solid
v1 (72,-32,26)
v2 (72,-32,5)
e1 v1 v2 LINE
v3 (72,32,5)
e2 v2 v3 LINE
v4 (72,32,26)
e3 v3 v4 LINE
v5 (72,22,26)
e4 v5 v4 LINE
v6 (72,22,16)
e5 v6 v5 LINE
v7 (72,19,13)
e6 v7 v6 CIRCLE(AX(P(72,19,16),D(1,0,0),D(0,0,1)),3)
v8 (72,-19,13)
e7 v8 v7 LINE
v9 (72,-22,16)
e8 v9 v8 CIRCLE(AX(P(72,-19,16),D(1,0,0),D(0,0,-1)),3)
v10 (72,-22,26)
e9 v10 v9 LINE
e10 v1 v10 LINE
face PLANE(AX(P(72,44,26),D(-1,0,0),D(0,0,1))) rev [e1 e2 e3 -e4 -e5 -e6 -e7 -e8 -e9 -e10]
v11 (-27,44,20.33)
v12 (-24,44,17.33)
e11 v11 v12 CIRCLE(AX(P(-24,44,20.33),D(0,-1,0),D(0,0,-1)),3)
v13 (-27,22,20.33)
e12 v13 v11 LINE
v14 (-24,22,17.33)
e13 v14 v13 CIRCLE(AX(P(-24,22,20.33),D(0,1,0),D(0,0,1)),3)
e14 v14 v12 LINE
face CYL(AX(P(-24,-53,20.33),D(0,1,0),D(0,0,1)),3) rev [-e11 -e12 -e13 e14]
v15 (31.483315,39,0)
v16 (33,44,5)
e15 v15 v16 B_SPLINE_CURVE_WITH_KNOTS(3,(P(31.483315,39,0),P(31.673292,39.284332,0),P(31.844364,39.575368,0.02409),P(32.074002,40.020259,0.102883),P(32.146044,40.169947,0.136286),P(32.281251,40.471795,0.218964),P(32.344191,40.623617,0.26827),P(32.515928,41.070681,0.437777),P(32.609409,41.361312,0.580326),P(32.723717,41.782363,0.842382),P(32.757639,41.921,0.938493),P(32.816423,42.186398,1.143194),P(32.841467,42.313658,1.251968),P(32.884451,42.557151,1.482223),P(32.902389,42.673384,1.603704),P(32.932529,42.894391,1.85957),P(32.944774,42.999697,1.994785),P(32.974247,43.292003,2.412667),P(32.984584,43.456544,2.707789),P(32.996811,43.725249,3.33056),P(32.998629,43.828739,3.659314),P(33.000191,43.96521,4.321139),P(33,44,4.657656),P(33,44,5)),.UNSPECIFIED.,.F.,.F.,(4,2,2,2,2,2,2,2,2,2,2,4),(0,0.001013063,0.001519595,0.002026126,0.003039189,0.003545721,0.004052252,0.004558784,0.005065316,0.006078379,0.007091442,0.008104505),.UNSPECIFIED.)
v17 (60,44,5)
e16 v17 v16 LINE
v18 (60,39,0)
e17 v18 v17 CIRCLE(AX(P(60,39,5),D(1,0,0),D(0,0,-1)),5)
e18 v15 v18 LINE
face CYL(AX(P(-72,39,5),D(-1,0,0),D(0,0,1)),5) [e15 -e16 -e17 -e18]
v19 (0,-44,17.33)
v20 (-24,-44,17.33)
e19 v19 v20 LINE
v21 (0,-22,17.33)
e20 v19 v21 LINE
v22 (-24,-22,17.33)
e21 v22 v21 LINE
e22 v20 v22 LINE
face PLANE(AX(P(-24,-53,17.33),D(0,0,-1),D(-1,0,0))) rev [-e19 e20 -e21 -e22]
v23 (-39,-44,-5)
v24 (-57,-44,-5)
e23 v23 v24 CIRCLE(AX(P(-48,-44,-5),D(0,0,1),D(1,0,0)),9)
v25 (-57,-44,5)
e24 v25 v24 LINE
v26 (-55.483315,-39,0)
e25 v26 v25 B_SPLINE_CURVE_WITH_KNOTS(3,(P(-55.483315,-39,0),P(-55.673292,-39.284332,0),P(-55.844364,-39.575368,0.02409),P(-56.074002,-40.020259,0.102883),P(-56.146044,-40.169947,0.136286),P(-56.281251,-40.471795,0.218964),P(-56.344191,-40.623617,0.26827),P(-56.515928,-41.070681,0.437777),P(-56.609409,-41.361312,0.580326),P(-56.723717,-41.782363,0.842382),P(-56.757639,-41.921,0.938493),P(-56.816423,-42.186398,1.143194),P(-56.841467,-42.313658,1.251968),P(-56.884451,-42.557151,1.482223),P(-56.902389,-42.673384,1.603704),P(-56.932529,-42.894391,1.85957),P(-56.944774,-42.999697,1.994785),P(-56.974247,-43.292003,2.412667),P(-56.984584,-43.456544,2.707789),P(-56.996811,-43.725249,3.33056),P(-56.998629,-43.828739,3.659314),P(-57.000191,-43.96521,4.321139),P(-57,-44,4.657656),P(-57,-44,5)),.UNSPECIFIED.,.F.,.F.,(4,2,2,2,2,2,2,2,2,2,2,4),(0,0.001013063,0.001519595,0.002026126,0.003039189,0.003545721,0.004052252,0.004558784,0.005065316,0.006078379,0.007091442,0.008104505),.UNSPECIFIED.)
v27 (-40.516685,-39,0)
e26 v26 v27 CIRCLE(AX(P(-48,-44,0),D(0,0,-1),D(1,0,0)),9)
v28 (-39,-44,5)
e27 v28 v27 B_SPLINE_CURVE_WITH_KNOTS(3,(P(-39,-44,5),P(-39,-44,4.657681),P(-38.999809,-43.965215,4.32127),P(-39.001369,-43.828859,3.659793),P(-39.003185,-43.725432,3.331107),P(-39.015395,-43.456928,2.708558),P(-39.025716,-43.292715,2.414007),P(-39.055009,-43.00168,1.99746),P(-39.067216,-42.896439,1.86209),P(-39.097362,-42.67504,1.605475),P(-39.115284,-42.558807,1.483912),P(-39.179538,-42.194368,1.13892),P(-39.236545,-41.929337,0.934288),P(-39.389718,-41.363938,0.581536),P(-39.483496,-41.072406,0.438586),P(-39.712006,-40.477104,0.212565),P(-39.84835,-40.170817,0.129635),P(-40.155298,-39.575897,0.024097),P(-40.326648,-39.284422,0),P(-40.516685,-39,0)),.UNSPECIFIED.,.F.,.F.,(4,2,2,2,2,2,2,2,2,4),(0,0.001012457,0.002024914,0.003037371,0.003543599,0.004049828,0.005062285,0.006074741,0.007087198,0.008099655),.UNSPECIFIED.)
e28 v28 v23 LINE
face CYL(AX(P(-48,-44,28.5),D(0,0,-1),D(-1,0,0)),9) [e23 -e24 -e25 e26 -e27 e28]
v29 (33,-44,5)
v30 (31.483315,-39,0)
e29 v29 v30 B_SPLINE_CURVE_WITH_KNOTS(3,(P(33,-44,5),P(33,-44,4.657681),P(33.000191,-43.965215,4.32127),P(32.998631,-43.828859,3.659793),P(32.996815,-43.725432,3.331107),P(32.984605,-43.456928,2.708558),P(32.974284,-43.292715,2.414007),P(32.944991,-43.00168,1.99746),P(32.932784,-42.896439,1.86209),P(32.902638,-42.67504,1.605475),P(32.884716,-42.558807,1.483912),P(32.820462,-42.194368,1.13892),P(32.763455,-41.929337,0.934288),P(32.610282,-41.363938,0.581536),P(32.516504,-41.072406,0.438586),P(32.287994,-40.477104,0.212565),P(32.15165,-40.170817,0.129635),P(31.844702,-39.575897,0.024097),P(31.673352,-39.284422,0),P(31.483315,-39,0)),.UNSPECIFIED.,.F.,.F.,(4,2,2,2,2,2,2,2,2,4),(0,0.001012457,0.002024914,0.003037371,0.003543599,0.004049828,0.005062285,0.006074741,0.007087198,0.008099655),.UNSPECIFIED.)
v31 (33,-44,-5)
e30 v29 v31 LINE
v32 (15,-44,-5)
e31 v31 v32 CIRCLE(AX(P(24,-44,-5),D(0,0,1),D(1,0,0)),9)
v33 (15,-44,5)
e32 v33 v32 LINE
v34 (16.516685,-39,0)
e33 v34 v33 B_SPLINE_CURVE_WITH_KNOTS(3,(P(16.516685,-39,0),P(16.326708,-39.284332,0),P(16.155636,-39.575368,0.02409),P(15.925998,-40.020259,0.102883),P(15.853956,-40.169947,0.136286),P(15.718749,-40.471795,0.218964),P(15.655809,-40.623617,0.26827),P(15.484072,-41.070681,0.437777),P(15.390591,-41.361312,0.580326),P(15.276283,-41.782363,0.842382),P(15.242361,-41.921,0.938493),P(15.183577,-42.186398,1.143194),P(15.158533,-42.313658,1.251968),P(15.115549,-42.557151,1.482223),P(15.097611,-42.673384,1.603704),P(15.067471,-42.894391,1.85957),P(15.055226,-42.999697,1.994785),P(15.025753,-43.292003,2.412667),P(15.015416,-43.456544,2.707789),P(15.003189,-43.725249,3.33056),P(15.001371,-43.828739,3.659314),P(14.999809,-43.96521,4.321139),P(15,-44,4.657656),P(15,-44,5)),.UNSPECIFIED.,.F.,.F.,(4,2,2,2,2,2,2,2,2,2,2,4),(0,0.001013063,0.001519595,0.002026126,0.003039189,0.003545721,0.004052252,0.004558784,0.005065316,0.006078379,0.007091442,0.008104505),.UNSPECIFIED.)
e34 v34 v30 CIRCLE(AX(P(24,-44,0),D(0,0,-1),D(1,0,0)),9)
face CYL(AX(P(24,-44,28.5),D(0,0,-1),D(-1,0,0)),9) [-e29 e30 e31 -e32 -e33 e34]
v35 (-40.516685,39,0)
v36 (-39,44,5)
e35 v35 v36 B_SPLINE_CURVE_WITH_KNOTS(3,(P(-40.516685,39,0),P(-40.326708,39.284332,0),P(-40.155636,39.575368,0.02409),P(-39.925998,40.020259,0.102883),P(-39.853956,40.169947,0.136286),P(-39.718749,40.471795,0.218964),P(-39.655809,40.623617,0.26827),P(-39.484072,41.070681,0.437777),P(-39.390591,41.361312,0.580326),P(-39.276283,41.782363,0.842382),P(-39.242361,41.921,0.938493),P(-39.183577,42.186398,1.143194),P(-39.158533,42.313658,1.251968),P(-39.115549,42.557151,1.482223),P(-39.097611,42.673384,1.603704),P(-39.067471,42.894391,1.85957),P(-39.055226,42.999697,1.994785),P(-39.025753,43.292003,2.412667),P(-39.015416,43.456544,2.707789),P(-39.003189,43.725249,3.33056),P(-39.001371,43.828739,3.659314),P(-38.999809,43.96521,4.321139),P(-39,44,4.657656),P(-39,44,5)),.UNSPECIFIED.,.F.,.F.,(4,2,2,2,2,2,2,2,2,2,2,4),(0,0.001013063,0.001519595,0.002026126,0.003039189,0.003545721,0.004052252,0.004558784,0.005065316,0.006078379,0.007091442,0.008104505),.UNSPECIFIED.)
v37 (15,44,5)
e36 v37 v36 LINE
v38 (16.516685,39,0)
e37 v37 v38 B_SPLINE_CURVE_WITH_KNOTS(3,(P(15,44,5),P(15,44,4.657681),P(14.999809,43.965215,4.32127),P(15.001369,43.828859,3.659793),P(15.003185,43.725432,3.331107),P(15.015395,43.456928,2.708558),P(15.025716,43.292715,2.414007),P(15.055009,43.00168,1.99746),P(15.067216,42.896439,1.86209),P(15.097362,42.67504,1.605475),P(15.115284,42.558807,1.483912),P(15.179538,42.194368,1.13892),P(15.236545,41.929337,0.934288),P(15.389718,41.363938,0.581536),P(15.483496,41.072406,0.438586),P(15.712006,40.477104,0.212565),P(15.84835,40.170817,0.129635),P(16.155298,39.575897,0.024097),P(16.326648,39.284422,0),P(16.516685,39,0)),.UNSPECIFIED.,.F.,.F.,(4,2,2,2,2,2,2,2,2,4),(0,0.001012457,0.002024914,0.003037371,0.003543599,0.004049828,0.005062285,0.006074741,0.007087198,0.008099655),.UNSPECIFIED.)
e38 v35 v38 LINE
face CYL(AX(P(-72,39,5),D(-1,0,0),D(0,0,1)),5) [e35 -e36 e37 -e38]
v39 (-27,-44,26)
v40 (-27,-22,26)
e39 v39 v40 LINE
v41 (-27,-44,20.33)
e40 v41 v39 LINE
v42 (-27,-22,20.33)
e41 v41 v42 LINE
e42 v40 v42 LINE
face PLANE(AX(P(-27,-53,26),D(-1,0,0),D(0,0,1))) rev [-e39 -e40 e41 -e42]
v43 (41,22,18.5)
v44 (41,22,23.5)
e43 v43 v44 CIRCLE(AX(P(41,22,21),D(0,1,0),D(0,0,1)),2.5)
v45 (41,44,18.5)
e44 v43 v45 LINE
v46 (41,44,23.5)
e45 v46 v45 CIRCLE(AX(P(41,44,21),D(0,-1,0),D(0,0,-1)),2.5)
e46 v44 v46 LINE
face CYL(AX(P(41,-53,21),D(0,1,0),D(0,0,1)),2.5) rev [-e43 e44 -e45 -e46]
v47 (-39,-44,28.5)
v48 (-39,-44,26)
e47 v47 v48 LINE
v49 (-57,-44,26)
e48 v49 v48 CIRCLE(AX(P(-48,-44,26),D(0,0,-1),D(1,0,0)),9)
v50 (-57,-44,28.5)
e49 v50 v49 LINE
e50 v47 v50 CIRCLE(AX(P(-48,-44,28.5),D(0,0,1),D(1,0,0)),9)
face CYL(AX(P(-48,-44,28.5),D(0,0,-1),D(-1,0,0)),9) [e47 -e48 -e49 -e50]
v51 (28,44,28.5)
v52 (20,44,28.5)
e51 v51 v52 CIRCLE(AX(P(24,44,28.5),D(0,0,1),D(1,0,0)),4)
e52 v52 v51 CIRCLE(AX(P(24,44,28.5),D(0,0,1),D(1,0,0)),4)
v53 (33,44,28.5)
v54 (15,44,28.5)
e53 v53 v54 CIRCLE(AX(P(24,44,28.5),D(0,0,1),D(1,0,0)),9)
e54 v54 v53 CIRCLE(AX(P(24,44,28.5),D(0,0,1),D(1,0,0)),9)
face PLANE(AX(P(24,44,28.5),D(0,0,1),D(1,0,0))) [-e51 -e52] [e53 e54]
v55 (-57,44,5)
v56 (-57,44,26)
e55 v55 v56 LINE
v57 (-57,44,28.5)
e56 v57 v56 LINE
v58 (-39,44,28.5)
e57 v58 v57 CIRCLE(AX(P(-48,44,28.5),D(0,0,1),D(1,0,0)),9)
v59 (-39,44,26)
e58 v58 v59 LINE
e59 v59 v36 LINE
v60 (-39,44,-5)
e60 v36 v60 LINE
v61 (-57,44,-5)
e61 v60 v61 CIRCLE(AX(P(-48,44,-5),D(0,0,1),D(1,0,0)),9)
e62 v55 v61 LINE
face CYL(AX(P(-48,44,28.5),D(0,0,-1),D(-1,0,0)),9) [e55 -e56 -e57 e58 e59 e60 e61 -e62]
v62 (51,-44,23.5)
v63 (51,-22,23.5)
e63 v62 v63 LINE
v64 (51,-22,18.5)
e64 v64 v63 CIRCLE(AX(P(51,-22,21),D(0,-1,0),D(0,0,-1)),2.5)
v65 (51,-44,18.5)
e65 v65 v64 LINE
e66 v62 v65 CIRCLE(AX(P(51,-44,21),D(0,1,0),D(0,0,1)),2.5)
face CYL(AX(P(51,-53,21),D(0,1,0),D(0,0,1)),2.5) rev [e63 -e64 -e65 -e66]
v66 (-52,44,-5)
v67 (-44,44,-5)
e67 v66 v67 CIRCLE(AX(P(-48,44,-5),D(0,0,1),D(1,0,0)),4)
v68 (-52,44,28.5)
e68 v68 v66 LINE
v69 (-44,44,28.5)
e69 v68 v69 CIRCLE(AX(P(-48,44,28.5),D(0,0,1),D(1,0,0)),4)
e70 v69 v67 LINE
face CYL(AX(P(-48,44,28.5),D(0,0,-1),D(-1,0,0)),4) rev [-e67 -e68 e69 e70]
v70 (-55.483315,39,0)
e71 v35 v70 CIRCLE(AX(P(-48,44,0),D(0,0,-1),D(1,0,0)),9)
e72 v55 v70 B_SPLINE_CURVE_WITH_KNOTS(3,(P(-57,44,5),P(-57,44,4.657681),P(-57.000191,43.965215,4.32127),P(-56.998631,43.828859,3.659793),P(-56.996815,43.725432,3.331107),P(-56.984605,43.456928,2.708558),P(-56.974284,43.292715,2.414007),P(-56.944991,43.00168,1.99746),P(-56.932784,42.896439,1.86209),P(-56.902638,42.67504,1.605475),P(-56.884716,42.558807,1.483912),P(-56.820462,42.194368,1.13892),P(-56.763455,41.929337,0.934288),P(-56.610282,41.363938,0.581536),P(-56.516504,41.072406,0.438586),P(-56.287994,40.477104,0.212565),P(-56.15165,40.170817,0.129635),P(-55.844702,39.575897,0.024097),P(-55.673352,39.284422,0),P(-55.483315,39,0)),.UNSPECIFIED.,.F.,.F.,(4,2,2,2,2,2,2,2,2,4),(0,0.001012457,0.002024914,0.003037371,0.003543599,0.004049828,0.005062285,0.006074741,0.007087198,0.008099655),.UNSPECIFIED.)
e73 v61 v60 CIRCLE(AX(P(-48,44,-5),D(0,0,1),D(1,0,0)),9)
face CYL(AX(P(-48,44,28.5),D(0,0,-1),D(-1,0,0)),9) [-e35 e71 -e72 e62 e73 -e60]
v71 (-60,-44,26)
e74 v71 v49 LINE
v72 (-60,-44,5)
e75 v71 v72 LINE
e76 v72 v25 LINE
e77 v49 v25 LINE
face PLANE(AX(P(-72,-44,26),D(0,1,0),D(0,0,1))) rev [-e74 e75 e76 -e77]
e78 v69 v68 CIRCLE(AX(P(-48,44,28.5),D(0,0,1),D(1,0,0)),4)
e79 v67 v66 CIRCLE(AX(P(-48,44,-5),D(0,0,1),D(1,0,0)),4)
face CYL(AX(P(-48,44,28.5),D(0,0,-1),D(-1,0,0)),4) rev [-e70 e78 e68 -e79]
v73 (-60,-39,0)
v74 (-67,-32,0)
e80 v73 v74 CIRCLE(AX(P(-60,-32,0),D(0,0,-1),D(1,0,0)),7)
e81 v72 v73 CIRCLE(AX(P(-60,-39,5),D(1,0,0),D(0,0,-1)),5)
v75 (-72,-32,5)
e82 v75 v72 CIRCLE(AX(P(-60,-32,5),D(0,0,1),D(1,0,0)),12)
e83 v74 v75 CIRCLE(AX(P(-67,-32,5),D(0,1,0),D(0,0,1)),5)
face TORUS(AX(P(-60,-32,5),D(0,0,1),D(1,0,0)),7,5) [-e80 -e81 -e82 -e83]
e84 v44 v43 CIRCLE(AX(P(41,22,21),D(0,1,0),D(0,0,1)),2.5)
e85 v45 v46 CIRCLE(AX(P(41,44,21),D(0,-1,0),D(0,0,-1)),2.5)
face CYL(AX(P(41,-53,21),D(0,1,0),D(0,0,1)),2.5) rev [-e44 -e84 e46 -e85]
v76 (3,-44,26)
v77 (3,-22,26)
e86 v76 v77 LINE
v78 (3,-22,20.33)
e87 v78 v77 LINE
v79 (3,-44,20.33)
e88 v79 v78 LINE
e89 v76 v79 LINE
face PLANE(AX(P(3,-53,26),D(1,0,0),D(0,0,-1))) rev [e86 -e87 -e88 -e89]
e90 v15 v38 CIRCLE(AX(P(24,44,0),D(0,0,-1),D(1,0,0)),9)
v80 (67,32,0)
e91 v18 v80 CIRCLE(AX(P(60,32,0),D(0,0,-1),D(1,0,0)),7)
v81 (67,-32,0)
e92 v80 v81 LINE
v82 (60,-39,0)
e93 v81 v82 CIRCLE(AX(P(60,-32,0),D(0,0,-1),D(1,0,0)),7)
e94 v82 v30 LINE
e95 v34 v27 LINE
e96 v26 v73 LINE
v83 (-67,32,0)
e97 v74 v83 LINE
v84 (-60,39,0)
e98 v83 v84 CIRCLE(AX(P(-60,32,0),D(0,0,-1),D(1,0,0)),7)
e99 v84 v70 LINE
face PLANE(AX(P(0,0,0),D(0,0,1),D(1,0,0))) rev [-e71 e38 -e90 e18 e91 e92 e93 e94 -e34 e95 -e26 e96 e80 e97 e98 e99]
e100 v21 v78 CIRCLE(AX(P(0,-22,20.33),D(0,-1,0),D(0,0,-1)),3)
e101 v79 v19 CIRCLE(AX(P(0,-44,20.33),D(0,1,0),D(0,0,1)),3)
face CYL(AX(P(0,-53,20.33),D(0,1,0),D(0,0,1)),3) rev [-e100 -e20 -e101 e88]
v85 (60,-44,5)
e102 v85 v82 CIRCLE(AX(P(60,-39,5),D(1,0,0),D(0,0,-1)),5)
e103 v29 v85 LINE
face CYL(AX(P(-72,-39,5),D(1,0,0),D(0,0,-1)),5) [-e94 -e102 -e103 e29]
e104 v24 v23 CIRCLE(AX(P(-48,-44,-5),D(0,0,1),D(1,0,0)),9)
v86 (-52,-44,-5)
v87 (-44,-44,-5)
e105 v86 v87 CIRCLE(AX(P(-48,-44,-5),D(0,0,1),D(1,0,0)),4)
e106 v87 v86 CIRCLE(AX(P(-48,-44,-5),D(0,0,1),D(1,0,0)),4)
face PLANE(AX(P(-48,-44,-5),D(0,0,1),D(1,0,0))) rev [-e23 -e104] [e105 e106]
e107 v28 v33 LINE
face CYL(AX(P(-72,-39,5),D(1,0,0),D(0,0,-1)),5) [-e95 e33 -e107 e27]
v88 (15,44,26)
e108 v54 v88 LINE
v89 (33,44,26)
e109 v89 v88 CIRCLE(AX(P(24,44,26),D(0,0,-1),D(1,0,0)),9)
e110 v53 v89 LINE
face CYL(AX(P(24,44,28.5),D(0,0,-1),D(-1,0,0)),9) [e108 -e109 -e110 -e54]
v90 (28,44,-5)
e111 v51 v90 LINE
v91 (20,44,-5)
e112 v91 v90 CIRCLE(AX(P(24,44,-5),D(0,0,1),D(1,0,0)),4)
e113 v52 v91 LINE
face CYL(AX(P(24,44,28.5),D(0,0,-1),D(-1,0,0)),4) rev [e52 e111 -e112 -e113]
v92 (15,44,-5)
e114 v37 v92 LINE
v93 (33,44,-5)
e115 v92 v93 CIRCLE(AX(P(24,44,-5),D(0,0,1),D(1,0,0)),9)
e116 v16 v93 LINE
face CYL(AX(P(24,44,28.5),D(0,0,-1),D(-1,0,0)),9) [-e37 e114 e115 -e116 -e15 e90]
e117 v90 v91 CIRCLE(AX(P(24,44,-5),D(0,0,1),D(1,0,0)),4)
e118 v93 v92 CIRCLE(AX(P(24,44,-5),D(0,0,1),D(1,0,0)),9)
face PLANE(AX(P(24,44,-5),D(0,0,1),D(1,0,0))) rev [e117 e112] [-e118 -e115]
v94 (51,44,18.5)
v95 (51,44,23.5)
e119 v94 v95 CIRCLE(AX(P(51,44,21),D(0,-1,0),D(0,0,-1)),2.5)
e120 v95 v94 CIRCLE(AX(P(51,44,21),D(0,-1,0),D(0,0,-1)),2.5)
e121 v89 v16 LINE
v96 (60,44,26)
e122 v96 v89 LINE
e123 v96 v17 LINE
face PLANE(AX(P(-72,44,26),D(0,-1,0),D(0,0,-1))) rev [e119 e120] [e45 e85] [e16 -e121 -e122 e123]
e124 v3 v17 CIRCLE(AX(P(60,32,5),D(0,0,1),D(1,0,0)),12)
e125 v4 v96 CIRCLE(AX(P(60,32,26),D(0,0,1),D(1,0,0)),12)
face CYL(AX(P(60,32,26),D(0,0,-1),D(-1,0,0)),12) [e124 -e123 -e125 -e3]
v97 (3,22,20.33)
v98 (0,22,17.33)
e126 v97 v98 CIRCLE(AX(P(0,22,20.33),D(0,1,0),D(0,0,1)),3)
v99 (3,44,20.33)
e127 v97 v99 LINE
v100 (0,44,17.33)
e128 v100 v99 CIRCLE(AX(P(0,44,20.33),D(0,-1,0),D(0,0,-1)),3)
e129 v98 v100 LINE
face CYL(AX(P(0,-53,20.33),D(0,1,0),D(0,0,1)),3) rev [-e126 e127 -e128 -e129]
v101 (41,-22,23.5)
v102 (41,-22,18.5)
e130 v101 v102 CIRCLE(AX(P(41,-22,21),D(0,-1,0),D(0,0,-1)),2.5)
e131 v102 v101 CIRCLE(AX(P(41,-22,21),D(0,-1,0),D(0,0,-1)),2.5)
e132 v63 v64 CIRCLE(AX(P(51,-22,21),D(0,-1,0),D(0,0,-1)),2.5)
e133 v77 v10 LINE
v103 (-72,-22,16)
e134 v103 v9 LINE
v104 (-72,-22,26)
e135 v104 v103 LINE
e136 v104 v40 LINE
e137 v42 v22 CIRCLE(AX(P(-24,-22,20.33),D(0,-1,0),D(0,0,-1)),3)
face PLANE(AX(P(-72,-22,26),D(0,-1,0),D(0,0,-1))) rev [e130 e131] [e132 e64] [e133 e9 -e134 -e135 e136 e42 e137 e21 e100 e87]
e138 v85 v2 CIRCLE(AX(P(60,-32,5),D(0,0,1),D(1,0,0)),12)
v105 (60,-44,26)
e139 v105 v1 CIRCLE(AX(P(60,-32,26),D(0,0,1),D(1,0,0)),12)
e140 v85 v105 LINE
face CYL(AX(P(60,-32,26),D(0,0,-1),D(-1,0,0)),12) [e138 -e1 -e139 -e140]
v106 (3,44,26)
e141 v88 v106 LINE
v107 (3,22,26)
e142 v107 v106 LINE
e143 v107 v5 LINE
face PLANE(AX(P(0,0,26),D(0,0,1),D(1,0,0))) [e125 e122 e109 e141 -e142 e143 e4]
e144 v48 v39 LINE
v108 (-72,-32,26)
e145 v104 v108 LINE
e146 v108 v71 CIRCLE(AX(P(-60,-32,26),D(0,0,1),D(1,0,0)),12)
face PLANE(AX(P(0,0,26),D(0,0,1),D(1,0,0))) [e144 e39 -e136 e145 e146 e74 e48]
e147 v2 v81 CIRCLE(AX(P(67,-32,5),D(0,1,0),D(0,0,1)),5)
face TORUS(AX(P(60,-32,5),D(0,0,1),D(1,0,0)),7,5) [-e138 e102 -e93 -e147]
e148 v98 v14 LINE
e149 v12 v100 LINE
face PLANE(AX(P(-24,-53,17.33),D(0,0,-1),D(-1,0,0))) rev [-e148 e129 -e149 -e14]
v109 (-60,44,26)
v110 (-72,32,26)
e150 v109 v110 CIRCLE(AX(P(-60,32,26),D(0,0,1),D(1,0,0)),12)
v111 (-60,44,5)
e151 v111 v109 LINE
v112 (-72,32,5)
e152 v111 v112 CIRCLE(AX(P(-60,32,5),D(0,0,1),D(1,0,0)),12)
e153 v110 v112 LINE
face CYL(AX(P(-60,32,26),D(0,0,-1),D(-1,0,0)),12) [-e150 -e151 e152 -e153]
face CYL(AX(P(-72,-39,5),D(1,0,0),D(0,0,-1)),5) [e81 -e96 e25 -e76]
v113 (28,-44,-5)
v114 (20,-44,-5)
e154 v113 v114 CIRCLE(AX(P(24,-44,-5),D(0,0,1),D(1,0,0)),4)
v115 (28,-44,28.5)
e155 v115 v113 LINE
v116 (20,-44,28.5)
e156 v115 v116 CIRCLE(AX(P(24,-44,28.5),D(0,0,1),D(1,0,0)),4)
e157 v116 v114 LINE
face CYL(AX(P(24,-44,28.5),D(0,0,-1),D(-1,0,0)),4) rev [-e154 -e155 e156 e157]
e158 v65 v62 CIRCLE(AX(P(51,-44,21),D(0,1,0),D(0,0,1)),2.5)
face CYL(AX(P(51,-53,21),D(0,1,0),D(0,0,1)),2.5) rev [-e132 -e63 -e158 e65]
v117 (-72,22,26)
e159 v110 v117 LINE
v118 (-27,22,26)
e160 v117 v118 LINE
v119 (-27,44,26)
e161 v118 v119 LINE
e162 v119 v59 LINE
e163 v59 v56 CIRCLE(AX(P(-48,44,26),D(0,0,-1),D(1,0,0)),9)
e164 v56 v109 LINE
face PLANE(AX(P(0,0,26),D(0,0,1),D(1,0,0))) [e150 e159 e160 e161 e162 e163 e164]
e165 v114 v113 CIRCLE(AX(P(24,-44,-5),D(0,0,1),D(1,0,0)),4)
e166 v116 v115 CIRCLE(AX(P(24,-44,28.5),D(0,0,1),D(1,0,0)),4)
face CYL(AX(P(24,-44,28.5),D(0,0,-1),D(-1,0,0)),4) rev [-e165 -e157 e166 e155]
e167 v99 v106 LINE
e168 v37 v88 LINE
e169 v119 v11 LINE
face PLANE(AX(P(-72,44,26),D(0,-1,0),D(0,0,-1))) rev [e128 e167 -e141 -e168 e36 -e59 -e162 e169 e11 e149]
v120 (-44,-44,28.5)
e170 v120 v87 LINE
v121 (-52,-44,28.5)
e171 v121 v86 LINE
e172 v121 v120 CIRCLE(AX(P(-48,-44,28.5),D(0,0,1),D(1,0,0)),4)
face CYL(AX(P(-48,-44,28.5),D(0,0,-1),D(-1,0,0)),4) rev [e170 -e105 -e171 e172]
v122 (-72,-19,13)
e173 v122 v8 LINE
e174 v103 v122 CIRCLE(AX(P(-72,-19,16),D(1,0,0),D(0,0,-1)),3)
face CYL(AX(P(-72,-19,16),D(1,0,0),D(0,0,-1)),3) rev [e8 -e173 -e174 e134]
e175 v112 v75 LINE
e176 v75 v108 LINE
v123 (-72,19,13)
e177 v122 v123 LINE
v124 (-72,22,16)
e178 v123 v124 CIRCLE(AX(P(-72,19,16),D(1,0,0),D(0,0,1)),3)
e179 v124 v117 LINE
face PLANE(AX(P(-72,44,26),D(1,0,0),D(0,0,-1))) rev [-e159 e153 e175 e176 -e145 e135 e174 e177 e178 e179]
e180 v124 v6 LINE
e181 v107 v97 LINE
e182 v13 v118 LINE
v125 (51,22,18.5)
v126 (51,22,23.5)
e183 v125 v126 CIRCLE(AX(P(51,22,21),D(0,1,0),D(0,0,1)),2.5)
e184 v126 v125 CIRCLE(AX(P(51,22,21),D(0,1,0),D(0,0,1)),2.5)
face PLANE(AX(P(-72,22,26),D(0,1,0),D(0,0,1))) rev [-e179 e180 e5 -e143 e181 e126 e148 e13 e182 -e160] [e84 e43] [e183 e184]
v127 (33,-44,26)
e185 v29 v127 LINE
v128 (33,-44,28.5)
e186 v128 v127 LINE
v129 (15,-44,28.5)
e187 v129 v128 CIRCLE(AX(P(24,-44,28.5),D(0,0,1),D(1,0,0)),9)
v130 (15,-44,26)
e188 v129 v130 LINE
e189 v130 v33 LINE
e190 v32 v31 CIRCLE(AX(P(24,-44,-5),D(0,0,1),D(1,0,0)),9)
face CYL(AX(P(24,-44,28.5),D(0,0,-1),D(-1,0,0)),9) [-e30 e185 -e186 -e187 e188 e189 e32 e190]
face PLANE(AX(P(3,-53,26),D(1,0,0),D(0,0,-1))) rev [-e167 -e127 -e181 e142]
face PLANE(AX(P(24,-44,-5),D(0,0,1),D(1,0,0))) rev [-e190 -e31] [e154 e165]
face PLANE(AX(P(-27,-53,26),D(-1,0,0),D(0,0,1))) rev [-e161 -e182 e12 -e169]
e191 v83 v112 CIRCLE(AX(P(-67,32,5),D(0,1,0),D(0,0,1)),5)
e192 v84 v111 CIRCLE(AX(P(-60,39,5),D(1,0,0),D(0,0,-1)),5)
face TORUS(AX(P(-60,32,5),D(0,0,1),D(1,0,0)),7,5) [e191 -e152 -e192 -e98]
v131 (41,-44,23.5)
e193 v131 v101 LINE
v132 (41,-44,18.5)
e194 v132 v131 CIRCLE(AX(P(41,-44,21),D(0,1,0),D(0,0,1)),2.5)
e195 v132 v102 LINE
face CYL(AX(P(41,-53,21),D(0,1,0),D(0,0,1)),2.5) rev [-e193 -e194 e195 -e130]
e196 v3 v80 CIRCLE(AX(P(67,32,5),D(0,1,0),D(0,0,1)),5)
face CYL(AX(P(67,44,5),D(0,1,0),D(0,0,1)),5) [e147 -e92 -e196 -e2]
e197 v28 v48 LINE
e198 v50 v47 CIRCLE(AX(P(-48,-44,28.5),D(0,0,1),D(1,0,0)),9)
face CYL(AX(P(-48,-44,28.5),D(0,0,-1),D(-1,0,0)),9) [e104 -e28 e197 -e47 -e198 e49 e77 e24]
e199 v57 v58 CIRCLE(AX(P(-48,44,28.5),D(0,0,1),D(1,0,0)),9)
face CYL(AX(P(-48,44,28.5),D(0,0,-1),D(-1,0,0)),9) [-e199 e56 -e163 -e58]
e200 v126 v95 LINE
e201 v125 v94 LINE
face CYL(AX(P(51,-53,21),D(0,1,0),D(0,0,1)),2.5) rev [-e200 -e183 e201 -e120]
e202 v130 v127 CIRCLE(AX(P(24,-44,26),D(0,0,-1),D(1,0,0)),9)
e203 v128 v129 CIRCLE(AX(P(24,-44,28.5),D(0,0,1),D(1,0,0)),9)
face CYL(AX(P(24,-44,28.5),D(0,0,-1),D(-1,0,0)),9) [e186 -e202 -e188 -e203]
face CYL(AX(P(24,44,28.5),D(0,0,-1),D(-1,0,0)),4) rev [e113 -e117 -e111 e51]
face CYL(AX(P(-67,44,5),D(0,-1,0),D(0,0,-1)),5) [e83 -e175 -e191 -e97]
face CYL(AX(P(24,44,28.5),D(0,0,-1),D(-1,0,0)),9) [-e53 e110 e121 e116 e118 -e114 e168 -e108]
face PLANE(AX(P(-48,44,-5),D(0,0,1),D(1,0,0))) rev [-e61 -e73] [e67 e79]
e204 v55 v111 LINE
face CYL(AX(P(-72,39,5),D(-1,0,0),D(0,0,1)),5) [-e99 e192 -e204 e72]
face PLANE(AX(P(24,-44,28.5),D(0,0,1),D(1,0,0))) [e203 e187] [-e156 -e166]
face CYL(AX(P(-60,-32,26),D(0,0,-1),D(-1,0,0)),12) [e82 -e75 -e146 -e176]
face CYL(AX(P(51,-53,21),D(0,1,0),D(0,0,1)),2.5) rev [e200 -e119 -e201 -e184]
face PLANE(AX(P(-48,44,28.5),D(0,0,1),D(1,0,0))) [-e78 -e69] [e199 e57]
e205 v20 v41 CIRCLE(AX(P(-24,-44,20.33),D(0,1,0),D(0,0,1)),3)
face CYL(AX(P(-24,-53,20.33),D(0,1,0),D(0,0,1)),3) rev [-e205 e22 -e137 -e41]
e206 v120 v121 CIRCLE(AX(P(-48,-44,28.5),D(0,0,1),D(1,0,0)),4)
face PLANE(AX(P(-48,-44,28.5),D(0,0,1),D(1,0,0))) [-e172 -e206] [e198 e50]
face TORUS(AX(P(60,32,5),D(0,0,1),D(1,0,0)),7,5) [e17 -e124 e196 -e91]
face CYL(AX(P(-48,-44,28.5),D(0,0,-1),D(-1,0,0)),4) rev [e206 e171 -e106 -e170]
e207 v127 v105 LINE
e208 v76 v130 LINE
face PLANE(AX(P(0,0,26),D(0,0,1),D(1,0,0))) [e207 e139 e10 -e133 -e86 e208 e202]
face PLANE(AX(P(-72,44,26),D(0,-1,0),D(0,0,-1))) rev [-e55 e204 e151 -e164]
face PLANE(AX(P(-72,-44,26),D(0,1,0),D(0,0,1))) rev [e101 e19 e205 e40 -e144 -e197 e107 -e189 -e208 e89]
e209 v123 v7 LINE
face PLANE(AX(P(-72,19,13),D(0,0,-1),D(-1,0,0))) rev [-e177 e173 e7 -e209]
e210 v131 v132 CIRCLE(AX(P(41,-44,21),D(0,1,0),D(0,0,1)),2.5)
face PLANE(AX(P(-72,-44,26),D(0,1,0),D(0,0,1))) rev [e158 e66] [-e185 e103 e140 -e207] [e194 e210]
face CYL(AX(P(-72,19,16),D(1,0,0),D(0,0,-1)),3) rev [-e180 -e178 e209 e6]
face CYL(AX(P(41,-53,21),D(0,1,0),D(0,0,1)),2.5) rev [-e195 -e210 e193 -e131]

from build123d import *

# Parameters (mm, degrees)
BASE_PLATE_SKETCH_W                      = 144
BASE_PLATE_SKETCH_H                      = 88
BASE_PLATE_144X88_DEPTH                  = 26
PLATE_CORNER_FILLETS_R12_R               = 12
PLATE_EDGE_FILLETS_R5_R                  = 5
CORNER_BOSSES_DEPTH                      = 28.5
CORNER_BOSSES_DEPTH_BACK                 = 5
CORNER_BOSS_SKETCH_R                     = 9
CORNER_BOSS_SKETCH_R_2                   = 4
CORNER_BOSS_HOLES_DEPTH                  = 94.836293705
CORNER_BOSS_HOLES_DEPTH_BACK             = 94.836293705
SKETCH3_2_R                              = 4
CENTER_CHANNEL_CUT_DEPTH                 = 94.836293705
CENTER_CHANNEL_CUT_DEPTH_BACK            = 94.836293705
SIDE_RAIL_SLOTS_AND_PIN_HOLES_DEPTH      = 94.836293705
SIDE_RAIL_SLOTS_AND_PIN_HOLES_DEPTH_BACK = 94.836293705
SIDE_RAIL_SLOT_SKETCH_R                  = 2.5


with BuildPart() as part:
    # Base Plate Sketch → Base Plate 144x88 (new body)
    with BuildSketch(Plane.XY):
        Rectangle(BASE_PLATE_SKETCH_W, BASE_PLATE_SKETCH_H)
    extrude(amount=BASE_PLATE_144X88_DEPTH)

    # Plate Corner Fillets R12
    plate_corner_fillets_r12_edges = [part.edges().sort_by_distance(p)[0] for p in [
        (72, -44, 13),
        (-72, -44, 13),
        (-72, 44, 13),
        (72, 44, 13),
    ]]
    fillet(plate_corner_fillets_r12_edges, radius=PLATE_CORNER_FILLETS_R12_R)

    # Plate Edge Fillets R5
    plate_edge_fillets_r5_edges = [part.edges().sort_by_distance(p)[0] for p in [
        (72, 0, 0),
        (0, -44, 0),
        (-72, 0, 0),
        (0, 44, 0),
        (68.485281374, 40.485281374, 0),
        (-68.485281374, 40.485281374, 0),
        (-68.485281374, -40.485281374, 0),
        (68.485281374, -40.485281374, 0),
    ]]
    fillet(plate_edge_fillets_r5_edges, radius=PLATE_EDGE_FILLETS_R5_R)

    # Corner Boss Sketch → Corner Bosses (add, two sides: drawn at the far end of the back side and taken through both)
    # profile 1 of 4: a face of its own
    with BuildSketch(Plane.XY.offset(-CORNER_BOSSES_DEPTH_BACK)):
        with Locations((24, 44)):
            Circle(CORNER_BOSS_SKETCH_R)
        with Locations((24, 44)):
            Circle(CORNER_BOSS_SKETCH_R_2, mode=Mode.SUBTRACT)
    # profile 2 of 4: a face of its own
    with BuildSketch(Plane.XY.offset(-CORNER_BOSSES_DEPTH_BACK)):
        with Locations((-48, 44)):
            Circle(CORNER_BOSS_SKETCH_R)
        with Locations((-48, 44)):
            Circle(CORNER_BOSS_SKETCH_R_2, mode=Mode.SUBTRACT)
    # profile 3 of 4: a face of its own
    with BuildSketch(Plane.XY.offset(-CORNER_BOSSES_DEPTH_BACK)):
        with Locations((-48, -44)):
            Circle(CORNER_BOSS_SKETCH_R)
        with Locations((-48, -44)):
            Circle(CORNER_BOSS_SKETCH_R_2, mode=Mode.SUBTRACT)
    # profile 4 of 4: a face of its own
    with BuildSketch(Plane.XY.offset(-CORNER_BOSSES_DEPTH_BACK)):
        with Locations((24, -44)):
            Circle(CORNER_BOSS_SKETCH_R)
        with Locations((24, -44)):
            Circle(CORNER_BOSS_SKETCH_R_2, mode=Mode.SUBTRACT)
    extrude(amount=CORNER_BOSSES_DEPTH + CORNER_BOSSES_DEPTH_BACK)

    # Sketch3_2 → Corner Boss Holes (cut, two sides: drawn at the far end of the back side and taken through both)
    with BuildSketch(Plane.XY.offset(-CORNER_BOSS_HOLES_DEPTH_BACK)):
        with Locations(Location((24, 44, 0), (0, 0, 180))):
            Circle(SKETCH3_2_R)
        with Locations(Location((-48, 44, 0), (0, 0, 180))):
            Circle(SKETCH3_2_R)
        with Locations(Location((-48, -44, 0), (0, 0, 180))):
            Circle(SKETCH3_2_R)
        with Locations(Location((24, -44, 0), (0, 0, 180))):
            Circle(SKETCH3_2_R)
    extrude(amount=CORNER_BOSS_HOLES_DEPTH + CORNER_BOSS_HOLES_DEPTH_BACK, mode=Mode.SUBTRACT)


with BuildPart() as corner_boss_holes_kept_piece:
    # of the separate pieces the step leaves, the one the design keeps (corner_boss_holes_pieces_kept)
    add(part.part.solids().sort_by_distance((60, 39, 0))[0])

    # Center Channel Sketch → Center Channel Cut (cut, two sides: drawn at the far end of the back side and taken through both)
    with BuildSketch(Plane(origin=(0, 0, 0), x_dir=(0, 0, -1), z_dir=(1, 0, 0)).offset(-CENTER_CHANNEL_CUT_DEPTH_BACK)):
        with BuildLine():
            Line((-26, 22), (-16, 22))
            ThreePointArc((-16, 22), (-13.878679656, 21.121320344), (-13, 19))
            Line((-13, 19), (-13, -19))
            ThreePointArc((-13, -19), (-13.878679656, -21.121320344), (-16, -22))
            Line((-16, -22), (-26, -22))
            Line((-26, -22), (-26, 22))
        make_face()
    extrude(amount=CENTER_CHANNEL_CUT_DEPTH + CENTER_CHANNEL_CUT_DEPTH_BACK, mode=Mode.SUBTRACT)

    # Side Rail Slot Sketch → Side Rail Slots and Pin Holes (cut, two sides: drawn at the far end of the back side and taken through both)
    with BuildSketch(Plane(origin=(0, 0, 0), x_dir=(1, 0, 0), z_dir=(0, 1, 0)).offset(-SIDE_RAIL_SLOTS_AND_PIN_HOLES_DEPTH_BACK)):
        with Locations(Location((51, -21, 0), (0, 0, 270))):
            Circle(SIDE_RAIL_SLOT_SKETCH_R)
        with Locations(Location((41, -21, 0), (0, 0, 270))):
            Circle(SIDE_RAIL_SLOT_SKETCH_R)
        with BuildLine():
            Line((-27, -26), (3, -26))
            Line((3, -26), (3, -20.33))
            ThreePointArc((3, -20.33), (2.121320344, -18.208679656), (0, -17.33))
            Line((0, -17.33), (-24, -17.33))
            ThreePointArc((-24, -17.33), (-26.121320344, -18.208679656), (-27, -20.33))
            Line((-27, -20.33), (-27, -26))
        make_face()
    extrude(amount=SIDE_RAIL_SLOTS_AND_PIN_HOLES_DEPTH + SIDE_RAIL_SLOTS_AND_PIN_HOLES_DEPTH_BACK, mode=Mode.SUBTRACT)


solid = corner_boss_holes_kept_piece.part
